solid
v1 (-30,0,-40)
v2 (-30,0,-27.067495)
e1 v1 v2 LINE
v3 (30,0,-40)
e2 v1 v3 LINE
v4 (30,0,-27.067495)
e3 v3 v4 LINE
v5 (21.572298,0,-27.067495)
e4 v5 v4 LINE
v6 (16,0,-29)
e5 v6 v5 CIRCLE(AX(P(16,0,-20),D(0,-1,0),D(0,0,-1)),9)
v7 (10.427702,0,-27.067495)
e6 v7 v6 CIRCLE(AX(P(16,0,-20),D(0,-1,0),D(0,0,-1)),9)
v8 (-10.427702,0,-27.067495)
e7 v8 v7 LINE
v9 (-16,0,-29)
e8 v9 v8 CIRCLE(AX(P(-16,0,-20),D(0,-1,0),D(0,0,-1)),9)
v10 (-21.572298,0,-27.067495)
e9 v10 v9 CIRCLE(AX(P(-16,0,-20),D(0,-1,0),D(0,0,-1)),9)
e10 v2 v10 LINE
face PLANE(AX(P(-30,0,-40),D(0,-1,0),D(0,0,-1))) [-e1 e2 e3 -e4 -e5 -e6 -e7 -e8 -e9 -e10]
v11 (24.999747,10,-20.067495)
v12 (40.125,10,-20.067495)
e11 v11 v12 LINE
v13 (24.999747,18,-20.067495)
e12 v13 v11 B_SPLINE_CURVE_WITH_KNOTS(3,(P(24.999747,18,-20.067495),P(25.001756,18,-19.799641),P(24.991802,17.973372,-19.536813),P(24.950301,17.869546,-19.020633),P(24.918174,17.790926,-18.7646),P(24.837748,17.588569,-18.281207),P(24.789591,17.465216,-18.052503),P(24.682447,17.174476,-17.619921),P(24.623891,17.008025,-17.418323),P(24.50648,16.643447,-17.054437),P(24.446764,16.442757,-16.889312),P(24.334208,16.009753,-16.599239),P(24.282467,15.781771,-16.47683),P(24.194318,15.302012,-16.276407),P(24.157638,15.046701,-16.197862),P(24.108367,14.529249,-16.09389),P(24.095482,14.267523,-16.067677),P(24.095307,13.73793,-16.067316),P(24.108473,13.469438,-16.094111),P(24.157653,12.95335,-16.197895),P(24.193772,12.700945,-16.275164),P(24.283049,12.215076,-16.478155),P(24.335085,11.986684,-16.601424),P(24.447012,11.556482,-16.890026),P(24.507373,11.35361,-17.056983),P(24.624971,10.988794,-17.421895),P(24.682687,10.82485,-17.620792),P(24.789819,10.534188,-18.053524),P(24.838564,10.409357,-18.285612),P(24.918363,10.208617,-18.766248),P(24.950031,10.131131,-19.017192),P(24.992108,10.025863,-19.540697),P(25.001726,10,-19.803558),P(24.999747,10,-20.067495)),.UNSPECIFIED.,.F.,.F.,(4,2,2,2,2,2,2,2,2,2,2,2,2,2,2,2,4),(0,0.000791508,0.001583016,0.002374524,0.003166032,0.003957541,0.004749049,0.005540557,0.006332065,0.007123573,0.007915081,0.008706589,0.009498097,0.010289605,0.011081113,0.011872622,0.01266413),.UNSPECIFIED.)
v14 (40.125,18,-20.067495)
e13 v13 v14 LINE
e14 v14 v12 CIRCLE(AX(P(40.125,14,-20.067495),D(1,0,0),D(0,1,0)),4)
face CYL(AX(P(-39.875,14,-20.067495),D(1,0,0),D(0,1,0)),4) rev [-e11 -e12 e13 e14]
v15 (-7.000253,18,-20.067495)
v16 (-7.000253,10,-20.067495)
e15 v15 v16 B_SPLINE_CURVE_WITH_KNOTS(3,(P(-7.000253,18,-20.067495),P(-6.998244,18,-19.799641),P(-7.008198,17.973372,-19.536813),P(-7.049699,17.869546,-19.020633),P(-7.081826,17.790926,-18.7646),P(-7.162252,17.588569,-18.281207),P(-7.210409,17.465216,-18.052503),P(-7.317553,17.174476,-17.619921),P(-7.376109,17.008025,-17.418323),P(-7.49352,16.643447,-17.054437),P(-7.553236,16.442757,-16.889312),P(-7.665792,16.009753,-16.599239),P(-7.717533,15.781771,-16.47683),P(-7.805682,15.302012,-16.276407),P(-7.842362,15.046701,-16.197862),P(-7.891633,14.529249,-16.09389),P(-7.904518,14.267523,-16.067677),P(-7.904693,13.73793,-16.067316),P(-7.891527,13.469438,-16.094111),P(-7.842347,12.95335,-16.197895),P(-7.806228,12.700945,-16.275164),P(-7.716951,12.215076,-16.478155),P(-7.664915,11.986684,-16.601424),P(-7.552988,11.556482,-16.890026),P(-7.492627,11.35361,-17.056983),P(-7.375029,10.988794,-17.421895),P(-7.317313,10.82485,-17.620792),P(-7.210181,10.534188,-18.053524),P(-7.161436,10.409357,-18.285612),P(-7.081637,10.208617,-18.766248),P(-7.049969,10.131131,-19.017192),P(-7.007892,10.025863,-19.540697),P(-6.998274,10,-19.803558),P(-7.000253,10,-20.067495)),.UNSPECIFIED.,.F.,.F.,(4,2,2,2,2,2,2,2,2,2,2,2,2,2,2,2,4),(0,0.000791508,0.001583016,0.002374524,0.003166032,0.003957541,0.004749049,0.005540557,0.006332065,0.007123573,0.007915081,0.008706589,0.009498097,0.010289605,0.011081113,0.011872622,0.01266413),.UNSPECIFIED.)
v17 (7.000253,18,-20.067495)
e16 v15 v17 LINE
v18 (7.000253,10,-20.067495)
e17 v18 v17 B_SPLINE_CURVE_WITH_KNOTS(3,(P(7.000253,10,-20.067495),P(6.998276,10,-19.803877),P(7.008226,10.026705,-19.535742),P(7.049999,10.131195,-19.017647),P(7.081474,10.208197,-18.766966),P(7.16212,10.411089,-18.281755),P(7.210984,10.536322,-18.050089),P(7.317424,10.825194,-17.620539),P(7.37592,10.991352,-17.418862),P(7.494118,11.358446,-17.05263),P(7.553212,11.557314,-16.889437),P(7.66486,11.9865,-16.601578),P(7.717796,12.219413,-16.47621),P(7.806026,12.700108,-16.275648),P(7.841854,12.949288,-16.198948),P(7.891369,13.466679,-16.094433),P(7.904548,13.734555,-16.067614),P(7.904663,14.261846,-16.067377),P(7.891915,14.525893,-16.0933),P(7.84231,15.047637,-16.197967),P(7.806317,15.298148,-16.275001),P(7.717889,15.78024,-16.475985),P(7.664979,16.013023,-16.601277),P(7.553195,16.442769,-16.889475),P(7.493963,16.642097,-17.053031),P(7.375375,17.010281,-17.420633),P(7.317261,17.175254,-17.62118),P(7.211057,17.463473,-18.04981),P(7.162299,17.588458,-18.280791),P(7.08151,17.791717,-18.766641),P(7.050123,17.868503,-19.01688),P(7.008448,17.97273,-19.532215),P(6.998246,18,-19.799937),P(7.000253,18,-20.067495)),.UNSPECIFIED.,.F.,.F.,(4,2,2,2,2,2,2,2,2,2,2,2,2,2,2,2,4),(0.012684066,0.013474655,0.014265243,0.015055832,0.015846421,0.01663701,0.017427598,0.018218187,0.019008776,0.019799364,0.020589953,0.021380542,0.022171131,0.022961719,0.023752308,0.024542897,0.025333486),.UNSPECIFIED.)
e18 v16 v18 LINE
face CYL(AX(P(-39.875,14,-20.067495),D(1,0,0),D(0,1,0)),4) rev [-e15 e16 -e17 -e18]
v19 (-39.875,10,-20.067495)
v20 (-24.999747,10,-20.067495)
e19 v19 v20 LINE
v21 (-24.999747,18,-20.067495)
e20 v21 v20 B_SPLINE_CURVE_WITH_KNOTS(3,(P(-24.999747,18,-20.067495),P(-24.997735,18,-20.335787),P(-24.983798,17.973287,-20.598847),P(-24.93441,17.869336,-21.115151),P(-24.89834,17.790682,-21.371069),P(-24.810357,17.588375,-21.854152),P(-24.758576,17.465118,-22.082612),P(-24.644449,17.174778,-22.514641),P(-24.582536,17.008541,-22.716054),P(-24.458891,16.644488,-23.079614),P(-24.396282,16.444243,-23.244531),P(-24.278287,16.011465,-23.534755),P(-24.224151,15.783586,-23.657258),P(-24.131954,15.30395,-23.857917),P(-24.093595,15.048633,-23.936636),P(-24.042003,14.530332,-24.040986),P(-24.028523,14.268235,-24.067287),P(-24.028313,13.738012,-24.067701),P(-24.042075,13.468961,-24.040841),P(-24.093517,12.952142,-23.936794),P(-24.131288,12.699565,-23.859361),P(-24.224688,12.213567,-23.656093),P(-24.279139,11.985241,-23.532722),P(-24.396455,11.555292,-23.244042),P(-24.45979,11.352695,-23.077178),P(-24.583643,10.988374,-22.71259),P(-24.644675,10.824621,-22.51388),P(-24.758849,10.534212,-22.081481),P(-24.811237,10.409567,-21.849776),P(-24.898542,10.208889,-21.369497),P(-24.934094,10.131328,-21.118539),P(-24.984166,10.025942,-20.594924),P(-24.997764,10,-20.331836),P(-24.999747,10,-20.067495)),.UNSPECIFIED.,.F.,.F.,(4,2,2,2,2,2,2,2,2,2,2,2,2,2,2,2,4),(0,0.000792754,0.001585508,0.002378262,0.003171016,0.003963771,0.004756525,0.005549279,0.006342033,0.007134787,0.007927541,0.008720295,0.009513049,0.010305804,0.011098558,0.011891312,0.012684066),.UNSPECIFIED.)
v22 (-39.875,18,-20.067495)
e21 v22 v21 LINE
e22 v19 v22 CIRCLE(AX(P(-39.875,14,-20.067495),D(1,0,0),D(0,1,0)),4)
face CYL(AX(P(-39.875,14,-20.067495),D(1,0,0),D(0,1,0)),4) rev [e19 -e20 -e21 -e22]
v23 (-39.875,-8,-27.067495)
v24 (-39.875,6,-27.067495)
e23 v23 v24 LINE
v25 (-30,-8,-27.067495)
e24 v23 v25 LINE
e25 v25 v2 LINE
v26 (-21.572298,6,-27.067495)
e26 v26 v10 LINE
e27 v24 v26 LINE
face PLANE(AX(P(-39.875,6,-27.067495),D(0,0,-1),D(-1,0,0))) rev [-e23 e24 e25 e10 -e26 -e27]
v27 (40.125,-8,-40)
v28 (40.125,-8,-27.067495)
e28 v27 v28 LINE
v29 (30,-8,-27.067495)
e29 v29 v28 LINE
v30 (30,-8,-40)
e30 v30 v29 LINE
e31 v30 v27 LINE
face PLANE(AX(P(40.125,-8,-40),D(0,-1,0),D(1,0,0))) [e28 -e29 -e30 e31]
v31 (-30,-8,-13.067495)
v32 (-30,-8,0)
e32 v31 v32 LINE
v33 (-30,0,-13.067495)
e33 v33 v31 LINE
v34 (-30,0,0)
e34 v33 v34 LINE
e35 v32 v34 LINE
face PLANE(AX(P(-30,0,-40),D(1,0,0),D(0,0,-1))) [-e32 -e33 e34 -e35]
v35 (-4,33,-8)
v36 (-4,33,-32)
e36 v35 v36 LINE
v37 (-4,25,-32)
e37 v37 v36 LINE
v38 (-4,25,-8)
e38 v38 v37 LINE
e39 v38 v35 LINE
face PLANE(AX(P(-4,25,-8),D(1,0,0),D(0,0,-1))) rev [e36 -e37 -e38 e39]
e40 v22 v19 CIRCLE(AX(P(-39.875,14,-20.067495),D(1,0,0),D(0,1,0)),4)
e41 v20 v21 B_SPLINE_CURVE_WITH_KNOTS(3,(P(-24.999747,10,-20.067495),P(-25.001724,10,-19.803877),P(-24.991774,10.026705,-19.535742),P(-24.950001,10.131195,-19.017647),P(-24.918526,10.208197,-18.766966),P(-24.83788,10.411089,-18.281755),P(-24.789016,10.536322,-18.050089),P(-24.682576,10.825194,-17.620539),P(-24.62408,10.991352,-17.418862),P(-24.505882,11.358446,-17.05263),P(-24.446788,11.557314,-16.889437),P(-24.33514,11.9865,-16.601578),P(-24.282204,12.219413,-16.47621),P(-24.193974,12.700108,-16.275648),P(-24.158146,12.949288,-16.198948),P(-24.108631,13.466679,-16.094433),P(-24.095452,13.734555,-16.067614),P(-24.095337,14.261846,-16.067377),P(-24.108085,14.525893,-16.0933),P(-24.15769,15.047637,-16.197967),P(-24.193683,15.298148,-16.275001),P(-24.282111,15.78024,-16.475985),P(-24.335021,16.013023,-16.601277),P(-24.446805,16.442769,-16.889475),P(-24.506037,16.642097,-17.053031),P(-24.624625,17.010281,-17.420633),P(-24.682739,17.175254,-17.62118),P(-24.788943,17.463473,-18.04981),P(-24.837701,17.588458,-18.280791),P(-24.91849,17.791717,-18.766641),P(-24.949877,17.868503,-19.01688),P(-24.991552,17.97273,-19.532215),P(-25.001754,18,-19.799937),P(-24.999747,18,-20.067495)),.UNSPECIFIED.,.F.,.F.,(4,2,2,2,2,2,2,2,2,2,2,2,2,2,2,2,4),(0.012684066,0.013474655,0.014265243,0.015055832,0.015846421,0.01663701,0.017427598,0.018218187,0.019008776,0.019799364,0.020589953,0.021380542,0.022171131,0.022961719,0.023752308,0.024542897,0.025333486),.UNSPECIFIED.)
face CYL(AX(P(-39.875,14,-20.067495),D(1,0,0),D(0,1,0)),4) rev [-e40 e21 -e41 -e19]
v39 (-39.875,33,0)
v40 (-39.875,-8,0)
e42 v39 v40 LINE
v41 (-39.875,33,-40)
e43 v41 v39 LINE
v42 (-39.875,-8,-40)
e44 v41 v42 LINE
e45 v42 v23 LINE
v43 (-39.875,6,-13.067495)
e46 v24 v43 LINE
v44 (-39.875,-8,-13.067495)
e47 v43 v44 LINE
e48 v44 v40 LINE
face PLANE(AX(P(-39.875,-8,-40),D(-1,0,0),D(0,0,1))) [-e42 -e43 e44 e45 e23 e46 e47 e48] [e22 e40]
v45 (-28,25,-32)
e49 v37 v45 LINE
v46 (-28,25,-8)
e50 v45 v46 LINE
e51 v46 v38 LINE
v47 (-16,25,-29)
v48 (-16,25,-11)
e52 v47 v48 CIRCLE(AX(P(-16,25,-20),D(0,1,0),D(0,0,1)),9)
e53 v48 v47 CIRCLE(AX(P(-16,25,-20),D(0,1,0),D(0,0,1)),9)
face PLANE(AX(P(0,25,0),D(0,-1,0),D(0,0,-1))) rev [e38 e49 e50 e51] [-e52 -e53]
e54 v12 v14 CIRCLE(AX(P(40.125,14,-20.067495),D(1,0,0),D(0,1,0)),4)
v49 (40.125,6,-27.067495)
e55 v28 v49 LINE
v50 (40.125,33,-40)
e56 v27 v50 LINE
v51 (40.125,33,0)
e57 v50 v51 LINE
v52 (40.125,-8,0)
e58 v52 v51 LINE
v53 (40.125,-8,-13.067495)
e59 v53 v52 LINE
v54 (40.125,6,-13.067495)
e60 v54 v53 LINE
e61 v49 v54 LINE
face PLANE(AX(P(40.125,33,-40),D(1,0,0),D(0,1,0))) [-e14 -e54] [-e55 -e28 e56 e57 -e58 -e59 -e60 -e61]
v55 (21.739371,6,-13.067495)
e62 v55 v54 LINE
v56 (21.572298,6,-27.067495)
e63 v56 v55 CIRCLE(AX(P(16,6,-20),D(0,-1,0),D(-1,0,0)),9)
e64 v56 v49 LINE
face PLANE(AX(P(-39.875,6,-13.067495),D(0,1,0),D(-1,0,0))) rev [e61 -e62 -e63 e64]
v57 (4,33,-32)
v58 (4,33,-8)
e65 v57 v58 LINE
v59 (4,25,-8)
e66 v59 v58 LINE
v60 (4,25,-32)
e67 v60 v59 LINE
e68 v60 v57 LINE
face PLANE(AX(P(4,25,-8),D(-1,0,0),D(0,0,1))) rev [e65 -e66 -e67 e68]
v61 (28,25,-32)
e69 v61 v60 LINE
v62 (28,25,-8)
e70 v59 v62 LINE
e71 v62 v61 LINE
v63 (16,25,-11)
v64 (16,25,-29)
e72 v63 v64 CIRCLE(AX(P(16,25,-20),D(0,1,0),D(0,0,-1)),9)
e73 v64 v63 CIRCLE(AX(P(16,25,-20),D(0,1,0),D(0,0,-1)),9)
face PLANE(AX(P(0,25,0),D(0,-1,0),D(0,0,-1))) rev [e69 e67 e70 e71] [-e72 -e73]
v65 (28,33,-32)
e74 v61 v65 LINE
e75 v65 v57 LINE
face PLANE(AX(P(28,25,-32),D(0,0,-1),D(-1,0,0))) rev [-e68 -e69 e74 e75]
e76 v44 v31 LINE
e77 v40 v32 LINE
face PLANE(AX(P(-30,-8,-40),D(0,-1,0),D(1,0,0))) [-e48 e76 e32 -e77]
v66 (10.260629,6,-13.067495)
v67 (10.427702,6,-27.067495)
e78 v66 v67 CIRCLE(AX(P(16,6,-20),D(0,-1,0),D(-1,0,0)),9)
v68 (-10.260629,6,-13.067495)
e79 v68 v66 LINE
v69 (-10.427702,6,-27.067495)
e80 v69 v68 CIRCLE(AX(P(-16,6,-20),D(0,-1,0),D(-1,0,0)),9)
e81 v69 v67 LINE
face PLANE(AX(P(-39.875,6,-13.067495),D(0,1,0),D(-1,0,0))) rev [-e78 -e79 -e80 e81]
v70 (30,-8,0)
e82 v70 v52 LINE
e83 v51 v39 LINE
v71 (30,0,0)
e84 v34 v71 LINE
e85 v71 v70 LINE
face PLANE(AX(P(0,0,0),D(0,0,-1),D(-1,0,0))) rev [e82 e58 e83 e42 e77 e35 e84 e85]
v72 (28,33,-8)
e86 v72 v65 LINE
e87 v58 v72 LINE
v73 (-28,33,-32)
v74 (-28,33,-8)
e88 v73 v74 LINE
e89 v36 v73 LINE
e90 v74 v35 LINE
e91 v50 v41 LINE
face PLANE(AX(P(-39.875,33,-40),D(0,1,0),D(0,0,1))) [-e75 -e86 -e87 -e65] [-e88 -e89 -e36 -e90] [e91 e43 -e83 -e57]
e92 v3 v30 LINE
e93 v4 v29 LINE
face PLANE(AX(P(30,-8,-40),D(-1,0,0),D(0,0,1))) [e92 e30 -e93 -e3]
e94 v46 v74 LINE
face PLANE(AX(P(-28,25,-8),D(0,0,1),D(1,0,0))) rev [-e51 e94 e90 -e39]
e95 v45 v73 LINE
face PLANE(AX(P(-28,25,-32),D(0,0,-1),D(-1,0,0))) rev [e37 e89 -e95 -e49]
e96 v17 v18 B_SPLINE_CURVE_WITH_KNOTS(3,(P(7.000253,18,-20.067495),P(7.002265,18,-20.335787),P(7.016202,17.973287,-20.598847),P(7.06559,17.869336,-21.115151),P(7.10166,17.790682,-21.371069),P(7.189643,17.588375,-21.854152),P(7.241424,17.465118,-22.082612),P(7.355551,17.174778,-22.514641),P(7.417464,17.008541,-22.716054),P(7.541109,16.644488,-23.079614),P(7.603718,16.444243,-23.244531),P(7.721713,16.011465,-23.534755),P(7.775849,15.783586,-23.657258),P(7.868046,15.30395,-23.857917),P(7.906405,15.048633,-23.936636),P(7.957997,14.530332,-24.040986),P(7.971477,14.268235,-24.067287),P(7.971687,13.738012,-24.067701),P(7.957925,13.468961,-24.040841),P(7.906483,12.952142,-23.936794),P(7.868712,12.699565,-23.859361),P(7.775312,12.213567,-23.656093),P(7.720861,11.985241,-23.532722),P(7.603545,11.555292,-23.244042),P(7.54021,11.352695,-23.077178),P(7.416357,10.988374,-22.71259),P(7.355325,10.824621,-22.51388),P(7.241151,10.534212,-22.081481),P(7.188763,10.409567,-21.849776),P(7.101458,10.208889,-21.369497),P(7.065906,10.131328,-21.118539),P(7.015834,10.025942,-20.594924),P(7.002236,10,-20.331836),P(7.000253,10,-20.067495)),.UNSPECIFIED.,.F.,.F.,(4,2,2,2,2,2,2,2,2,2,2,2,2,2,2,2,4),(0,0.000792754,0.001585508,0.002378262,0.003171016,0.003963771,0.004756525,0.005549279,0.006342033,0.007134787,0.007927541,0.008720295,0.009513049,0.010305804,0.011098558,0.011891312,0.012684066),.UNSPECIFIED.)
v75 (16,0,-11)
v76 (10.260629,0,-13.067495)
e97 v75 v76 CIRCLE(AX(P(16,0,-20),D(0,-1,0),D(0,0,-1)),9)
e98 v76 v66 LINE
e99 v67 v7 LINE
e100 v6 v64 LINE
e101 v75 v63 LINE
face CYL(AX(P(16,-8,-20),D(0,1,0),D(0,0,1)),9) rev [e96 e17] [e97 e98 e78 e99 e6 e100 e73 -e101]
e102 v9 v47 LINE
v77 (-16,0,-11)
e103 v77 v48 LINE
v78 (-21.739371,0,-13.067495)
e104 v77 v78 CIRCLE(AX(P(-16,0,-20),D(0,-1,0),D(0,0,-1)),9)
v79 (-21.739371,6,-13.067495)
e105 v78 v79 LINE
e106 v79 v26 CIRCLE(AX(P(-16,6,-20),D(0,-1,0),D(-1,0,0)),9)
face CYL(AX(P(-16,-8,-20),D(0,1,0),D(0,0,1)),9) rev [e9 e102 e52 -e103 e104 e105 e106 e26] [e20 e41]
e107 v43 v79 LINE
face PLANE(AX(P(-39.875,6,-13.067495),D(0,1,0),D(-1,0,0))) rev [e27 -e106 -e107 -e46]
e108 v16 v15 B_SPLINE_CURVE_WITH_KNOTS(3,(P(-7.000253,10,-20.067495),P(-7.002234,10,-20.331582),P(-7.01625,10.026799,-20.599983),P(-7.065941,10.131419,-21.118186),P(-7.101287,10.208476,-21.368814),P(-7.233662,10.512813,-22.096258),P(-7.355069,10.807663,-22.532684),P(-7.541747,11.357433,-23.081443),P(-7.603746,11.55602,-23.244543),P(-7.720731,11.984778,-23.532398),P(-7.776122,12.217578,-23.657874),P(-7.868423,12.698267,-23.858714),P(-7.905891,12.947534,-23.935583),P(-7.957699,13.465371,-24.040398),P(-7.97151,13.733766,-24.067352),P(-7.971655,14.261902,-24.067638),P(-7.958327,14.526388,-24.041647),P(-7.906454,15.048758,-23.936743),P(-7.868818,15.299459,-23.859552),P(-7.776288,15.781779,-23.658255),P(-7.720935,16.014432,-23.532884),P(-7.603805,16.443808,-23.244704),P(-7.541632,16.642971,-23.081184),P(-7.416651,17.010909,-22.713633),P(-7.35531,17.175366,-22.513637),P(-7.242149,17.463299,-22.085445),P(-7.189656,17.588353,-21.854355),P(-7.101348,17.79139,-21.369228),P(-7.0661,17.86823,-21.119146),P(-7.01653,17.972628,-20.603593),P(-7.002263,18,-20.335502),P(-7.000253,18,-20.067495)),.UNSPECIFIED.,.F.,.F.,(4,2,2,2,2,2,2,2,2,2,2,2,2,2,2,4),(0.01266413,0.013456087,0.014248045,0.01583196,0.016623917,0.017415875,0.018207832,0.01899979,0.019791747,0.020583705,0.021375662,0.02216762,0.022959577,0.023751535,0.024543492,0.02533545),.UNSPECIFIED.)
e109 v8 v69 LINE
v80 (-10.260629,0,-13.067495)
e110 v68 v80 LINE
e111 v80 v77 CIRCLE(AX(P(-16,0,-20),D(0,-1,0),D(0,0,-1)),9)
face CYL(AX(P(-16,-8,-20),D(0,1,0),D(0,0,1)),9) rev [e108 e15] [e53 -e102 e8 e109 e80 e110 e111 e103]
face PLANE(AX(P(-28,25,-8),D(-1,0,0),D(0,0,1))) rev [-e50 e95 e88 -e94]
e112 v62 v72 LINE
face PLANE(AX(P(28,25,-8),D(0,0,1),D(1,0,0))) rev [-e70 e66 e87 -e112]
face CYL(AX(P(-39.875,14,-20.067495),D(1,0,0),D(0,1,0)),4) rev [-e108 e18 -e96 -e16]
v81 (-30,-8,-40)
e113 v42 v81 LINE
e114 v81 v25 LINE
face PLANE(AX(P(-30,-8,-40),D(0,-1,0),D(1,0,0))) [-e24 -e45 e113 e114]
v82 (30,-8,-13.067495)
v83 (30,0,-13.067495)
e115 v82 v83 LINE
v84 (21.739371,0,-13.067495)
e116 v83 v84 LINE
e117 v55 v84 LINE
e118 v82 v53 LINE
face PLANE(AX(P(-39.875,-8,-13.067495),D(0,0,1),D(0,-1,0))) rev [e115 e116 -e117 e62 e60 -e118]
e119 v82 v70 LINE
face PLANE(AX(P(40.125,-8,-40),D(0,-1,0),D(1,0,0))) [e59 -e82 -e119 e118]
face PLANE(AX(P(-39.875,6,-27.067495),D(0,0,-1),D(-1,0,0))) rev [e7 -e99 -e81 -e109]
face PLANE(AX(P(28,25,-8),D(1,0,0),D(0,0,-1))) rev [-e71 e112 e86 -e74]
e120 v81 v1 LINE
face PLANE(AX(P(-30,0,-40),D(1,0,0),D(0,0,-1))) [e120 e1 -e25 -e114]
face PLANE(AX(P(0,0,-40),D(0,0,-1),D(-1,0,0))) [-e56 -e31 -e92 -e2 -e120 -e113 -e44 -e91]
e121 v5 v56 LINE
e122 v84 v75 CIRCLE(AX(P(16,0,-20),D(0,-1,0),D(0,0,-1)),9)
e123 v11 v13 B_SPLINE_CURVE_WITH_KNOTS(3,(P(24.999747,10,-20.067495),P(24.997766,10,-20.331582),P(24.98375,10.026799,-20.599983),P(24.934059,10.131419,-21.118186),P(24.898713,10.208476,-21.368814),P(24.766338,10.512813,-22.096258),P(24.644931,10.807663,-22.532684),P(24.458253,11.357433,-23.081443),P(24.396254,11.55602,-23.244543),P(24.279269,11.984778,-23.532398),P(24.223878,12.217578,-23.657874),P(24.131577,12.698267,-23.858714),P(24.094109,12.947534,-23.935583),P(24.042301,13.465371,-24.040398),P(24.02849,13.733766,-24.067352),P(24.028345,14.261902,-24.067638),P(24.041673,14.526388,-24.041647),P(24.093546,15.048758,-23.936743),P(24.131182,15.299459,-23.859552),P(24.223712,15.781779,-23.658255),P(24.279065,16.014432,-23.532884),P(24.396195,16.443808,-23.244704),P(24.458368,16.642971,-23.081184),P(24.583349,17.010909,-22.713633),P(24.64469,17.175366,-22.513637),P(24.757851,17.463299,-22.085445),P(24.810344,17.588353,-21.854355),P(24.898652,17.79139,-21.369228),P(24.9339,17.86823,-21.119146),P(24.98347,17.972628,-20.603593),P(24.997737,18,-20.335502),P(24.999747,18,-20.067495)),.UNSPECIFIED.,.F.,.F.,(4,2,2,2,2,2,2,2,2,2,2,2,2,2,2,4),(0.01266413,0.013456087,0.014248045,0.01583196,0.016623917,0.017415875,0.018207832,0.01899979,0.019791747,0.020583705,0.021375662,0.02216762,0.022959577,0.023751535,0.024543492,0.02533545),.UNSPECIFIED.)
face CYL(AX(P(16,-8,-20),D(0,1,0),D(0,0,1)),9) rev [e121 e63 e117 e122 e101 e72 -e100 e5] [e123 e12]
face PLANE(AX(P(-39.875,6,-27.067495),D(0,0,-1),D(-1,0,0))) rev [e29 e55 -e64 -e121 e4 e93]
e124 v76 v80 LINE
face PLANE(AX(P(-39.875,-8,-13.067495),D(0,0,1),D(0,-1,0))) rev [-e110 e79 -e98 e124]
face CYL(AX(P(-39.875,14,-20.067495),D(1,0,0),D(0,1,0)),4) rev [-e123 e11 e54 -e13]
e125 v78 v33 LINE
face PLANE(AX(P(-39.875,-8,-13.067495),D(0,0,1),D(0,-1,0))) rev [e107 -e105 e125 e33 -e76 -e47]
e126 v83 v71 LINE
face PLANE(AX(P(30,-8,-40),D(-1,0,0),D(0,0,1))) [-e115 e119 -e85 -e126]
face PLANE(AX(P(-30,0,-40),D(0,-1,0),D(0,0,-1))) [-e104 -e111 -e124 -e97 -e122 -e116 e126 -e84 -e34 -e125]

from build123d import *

# Parameters (mm, degrees)
BASE_BLOCK_40_DEPTH          = 40
SQUARE_POCKETS_SKETCH_W      = 24
SQUARE_POCKETS_SKETCH_H      = 24
SQUARE_POCKETS_2X24X24_DEPTH = 8
POCKET_HOLES_SKETCH_R        = 9
POCKET_HOLES_2X_12_DEPTH     = 66.566879024
END_BORE_AND_SLOT_SKETCH_R   = 4
END_BORE_AND_SLOT_SKETCH_W   = 14
END_BORE_AND_SLOT_SKETCH_H   = 14
END_BORE_AND_SLOT_DEPTH      = 96.336247042


with BuildPart() as part:
    # Block Profile Sketch → Base Block 40 (new body)
    with BuildSketch(Plane.XY):
        Polygon((-30, 0), (30, 0), (30, -8), (40.125, -8), (40.125, 33), (-39.875, 33), (-39.875, -8), (-30, -8), align=None)
    extrude(amount=-BASE_BLOCK_40_DEPTH)

    # Square Pockets Sketch → Square Pockets 2x24x24 (cut)
    with BuildSketch(Plane(origin=(0, 33, 0), x_dir=(1, 0, 0), z_dir=(0, 1, 0))):
        with Locations((-16, 20)):
            Rectangle(SQUARE_POCKETS_SKETCH_W, SQUARE_POCKETS_SKETCH_H)
        with Locations((16, 20)):
            Rectangle(SQUARE_POCKETS_SKETCH_W, SQUARE_POCKETS_SKETCH_H)
    extrude(amount=-SQUARE_POCKETS_2X24X24_DEPTH, mode=Mode.SUBTRACT)

    # Pocket Holes Sketch → Pocket Holes 2xØ12 (cut, through all)
    with BuildSketch(Plane(origin=(0, 25, 0), x_dir=(1, 0, 0), z_dir=(0, 1, 0))):
        with Locations(Location((-16, 20, 0), (0, 0, 270))):
            Circle(POCKET_HOLES_SKETCH_R)
        with Locations(Location((16, 20, 0), (0, 0, 90))):
            Circle(POCKET_HOLES_SKETCH_R)
    extrude(amount=-POCKET_HOLES_2X_12_DEPTH, mode=Mode.SUBTRACT)

    # End Bore and Slot Sketch → End Bore and Slot (cut, through all)
    with BuildSketch(Plane(origin=(40.125, 0, 0), x_dir=(0, 0, -1), z_dir=(1, 0, 0))):
        with Locations(Location((20.067495301, 14, 0), (0, 0, 90))):
            Circle(END_BORE_AND_SLOT_SKETCH_R)
        with Locations((20.067495301, -1)):
            Rectangle(END_BORE_AND_SLOT_SKETCH_W, END_BORE_AND_SLOT_SKETCH_H)
    extrude(amount=-END_BORE_AND_SLOT_DEPTH, mode=Mode.SUBTRACT)


solid = part.part
